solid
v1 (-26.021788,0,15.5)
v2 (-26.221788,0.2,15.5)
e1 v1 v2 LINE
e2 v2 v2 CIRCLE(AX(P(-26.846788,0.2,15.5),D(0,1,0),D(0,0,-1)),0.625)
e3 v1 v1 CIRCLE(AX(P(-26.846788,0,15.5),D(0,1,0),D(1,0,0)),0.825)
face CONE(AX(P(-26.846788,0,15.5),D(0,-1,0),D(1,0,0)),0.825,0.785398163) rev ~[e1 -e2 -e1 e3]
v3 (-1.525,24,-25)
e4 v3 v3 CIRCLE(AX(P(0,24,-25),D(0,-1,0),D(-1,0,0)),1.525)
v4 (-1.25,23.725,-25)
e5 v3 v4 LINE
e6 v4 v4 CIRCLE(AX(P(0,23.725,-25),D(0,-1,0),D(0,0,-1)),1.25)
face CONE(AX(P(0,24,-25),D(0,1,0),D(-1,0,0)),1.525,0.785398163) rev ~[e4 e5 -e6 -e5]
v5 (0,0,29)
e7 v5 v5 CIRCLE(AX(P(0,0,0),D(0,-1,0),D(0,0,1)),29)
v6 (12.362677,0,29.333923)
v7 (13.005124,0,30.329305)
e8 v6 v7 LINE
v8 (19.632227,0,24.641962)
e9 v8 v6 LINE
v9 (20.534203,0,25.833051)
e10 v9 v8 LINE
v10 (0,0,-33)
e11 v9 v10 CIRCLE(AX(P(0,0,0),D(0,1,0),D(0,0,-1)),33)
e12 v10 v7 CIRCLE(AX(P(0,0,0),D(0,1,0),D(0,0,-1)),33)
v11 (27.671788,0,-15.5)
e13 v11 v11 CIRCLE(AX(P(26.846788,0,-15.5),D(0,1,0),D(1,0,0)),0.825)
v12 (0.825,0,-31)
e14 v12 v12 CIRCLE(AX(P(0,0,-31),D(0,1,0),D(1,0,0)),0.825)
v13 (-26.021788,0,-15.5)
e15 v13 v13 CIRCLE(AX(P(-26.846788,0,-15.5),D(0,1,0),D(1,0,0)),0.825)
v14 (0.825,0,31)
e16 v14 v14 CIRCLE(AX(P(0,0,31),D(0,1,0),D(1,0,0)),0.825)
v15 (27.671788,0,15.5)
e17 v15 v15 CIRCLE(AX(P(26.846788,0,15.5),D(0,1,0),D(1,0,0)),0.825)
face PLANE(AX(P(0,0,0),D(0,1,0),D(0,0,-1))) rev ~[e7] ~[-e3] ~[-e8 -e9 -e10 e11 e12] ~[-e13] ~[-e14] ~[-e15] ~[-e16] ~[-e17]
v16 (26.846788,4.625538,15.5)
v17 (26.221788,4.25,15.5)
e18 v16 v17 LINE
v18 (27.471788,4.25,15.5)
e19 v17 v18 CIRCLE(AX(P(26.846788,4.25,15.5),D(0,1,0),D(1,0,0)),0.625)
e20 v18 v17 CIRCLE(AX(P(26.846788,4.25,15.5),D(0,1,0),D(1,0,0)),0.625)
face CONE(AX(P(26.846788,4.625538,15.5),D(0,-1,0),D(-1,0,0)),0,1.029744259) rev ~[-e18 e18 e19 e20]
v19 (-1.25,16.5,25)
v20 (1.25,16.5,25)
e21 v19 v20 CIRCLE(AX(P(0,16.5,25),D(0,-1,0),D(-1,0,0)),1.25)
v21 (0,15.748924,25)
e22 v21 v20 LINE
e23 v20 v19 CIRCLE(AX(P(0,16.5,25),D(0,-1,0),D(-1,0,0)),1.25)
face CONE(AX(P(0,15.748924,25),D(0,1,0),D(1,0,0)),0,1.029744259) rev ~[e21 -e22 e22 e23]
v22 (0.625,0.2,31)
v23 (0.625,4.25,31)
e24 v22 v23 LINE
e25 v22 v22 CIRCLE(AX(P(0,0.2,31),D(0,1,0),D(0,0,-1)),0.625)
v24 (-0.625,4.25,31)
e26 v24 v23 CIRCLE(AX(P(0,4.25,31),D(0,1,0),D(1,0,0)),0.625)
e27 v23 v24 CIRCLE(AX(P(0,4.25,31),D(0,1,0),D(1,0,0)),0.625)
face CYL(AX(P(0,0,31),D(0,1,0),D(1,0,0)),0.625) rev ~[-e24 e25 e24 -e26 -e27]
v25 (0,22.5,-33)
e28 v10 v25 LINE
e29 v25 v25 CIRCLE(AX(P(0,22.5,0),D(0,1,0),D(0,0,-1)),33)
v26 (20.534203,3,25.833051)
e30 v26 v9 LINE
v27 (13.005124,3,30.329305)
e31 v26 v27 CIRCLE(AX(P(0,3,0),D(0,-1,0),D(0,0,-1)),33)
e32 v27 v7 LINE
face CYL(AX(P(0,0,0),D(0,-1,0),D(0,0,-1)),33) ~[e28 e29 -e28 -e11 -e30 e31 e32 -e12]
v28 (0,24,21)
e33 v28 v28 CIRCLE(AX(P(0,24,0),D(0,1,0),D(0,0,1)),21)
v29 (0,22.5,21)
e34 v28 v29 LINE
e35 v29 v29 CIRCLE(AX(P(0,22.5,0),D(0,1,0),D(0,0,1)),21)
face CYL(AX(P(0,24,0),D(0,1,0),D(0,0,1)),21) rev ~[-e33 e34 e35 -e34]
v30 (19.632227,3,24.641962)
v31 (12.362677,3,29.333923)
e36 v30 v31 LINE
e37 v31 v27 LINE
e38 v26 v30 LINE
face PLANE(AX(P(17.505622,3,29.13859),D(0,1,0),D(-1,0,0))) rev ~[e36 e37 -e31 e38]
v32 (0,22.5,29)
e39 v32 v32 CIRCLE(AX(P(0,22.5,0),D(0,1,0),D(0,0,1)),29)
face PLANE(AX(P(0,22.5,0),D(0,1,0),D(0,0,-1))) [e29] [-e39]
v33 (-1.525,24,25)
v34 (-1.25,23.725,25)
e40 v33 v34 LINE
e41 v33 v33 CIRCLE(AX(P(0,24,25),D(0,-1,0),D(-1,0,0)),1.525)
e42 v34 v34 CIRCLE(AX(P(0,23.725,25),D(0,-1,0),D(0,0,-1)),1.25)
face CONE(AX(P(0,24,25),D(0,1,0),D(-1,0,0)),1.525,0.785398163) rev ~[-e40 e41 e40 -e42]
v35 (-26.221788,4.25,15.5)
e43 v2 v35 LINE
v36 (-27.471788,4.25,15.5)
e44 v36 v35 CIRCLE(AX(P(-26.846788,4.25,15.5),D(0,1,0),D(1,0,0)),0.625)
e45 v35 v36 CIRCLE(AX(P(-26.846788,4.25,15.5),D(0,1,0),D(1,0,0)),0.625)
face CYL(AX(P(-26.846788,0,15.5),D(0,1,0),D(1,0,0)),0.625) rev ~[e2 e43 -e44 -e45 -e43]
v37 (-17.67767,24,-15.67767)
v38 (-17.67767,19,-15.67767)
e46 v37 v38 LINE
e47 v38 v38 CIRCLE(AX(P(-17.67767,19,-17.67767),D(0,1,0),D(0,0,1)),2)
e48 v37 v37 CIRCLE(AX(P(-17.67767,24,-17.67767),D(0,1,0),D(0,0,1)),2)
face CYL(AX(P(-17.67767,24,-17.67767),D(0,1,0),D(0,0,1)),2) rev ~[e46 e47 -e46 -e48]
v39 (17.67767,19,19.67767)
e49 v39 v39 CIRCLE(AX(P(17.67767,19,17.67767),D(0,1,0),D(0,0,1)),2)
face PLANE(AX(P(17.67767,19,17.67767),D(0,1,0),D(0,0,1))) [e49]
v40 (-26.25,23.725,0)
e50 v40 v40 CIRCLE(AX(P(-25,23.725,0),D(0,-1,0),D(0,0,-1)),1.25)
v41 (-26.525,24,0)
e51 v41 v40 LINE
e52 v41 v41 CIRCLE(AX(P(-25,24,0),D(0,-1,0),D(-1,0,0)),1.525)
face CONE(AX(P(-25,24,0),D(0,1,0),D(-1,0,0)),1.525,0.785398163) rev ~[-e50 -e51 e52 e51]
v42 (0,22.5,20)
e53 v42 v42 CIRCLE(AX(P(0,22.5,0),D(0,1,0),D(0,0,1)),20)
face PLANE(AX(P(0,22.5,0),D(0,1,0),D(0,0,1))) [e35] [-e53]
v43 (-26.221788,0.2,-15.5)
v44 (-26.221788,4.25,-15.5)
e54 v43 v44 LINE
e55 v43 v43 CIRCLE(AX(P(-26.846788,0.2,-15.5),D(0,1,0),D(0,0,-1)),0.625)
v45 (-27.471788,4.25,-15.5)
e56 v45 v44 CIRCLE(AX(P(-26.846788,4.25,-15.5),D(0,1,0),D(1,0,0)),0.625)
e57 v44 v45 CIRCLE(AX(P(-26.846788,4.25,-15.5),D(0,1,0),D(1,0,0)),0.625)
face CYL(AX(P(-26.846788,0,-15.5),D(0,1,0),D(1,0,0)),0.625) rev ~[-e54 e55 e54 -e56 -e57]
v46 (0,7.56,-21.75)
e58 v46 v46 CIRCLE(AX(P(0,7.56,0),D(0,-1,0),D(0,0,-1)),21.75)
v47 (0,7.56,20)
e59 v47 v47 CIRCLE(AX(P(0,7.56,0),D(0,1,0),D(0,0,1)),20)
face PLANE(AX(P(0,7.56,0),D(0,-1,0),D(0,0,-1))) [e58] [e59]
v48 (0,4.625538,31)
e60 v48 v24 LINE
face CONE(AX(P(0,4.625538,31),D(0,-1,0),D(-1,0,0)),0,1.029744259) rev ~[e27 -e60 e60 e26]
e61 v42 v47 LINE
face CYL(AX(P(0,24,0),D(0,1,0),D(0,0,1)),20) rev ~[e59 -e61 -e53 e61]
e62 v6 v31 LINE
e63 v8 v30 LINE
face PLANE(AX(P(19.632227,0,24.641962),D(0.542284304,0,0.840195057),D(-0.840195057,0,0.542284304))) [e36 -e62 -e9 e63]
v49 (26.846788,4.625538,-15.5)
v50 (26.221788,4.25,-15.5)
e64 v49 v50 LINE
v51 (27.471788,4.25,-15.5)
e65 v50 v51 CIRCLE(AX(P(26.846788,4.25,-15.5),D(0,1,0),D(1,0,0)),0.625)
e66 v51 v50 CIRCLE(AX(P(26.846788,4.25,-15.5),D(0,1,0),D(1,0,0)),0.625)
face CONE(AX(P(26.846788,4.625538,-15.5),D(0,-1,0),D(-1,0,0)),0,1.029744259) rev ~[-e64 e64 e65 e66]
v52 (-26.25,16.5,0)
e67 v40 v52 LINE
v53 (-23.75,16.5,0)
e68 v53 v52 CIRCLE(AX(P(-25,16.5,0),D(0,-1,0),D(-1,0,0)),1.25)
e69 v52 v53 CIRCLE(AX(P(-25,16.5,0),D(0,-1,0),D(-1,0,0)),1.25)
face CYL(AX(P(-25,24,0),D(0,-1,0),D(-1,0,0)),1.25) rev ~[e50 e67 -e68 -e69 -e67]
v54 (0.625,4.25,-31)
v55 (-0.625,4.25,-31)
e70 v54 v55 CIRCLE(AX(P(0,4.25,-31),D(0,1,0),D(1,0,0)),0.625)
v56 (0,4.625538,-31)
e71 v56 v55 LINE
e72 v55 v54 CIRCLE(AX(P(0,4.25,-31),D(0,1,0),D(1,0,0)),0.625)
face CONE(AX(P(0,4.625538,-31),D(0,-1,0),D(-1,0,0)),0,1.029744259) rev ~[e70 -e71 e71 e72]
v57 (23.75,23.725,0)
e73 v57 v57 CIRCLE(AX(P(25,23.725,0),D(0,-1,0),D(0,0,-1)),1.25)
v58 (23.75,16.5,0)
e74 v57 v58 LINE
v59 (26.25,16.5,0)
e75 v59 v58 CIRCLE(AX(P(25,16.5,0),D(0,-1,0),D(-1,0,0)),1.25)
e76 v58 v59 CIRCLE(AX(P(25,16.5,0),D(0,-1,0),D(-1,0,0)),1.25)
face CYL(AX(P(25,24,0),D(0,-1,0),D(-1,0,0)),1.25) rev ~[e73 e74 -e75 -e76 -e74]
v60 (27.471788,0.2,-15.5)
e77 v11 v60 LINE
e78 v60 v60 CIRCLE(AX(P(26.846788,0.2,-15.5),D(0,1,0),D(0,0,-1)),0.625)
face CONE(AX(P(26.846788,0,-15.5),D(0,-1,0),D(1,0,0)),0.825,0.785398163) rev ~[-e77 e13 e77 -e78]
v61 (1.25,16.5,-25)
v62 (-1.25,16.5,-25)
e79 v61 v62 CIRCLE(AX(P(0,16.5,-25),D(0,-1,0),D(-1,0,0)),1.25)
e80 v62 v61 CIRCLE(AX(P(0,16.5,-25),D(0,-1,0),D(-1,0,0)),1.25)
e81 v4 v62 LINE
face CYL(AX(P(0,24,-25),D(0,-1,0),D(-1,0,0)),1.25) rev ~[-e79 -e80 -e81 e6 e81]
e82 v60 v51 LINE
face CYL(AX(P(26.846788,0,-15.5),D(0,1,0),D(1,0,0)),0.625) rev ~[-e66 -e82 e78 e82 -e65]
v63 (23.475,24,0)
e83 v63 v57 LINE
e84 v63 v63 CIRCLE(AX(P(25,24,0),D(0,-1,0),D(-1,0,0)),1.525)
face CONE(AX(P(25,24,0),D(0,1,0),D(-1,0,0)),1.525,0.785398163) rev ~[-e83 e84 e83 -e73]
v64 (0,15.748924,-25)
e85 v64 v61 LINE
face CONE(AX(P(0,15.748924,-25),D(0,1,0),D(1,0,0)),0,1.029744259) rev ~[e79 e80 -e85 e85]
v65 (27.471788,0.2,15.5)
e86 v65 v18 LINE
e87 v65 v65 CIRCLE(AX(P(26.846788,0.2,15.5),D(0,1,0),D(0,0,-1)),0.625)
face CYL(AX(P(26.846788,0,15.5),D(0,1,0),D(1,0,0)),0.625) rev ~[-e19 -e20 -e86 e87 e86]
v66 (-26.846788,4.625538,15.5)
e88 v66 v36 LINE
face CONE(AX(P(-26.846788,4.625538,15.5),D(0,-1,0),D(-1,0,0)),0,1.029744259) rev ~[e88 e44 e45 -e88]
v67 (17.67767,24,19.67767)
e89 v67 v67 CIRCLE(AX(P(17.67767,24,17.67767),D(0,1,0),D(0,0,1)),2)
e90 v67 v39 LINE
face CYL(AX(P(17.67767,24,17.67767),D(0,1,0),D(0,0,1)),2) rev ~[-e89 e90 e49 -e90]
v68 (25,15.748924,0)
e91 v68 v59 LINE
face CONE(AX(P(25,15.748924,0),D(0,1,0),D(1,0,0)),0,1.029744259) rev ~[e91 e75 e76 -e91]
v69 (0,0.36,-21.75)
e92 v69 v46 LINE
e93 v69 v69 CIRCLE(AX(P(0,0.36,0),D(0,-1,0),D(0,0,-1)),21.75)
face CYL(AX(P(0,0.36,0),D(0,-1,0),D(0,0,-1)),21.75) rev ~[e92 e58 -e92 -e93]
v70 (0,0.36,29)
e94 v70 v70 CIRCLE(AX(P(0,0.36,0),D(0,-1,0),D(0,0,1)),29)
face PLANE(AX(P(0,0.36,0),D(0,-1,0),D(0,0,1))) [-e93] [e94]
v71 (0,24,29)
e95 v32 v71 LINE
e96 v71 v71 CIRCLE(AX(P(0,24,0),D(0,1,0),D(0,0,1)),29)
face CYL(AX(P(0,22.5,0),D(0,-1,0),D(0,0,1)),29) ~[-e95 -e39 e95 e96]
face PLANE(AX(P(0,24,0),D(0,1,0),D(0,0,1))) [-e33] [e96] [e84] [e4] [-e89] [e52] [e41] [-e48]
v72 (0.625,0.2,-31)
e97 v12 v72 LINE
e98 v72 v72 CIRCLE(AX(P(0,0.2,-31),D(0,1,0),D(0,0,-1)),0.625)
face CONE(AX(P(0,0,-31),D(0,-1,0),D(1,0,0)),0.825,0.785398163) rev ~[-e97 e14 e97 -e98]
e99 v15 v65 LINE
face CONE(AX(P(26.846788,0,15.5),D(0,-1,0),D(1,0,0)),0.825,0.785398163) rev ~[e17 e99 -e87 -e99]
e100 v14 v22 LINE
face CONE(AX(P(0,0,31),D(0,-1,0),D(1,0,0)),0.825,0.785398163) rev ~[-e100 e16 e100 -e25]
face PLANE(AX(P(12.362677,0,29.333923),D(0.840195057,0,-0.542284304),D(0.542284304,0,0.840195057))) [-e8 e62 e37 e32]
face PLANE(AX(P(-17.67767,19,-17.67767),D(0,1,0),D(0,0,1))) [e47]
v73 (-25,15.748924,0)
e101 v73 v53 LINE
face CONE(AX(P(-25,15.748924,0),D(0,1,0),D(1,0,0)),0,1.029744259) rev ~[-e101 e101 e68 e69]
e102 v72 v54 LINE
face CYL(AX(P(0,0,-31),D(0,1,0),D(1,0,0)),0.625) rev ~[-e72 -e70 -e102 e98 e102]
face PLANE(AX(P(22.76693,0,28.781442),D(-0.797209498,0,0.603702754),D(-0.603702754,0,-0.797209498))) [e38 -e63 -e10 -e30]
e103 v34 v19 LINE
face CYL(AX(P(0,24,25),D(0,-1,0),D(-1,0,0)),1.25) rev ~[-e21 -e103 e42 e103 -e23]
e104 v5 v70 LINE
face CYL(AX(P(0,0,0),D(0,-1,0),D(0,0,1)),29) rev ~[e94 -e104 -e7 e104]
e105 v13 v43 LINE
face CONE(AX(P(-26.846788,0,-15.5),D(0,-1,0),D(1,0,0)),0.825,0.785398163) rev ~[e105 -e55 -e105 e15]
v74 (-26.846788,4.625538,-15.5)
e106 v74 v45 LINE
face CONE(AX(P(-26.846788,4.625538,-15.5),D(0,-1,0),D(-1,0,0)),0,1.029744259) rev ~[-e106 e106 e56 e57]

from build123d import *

# Parameters (mm, degrees)
SKETCH1_R                     = 33
BOSS_EXTRUDE1_DEPTH           = 22.5
SKETCH2_R                     = 29
BOSS_EXTRUDE2_DEPTH           = 1.5
SKETCH3_R                     = 20
CUT_EXTRUDE1_DEPTH            = 58.5
M3_TAPPED_HOLE1_D             = 2.5
M3_TAPPED_HOLE1_DEPTH         = 7.5
M3_TAPPED_HOLE1_CSINK_D       = 3.05
M3_TAPPED_HOLE1_CSINK_ANGLE   = 90
M3_TAPPED_HOLE1_TIP           = 0.751075774
SKETCH7_R                     = 2
CUT_EXTRUDE2_DEPTH            = 5
SKETCH8_R                     = 21
CUT_EXTRUDE3_DEPTH            = 1.5
SKETCH9_R                     = 29
CUT_EXTRUDE4_DEPTH            = 0.36
SKETCH10_R                    = 21.75
CUT_EXTRUDE5_DEPTH            = 7.2
M1_6_TAPPED_HOLE1_D           = 1.25
M1_6_TAPPED_HOLE1_DEPTH       = 4.25
M1_6_TAPPED_HOLE1_CSINK_D     = 1.65
M1_6_TAPPED_HOLE1_CSINK_ANGLE = 90
M1_6_TAPPED_HOLE1_TIP         = 0.375537887
CUT_EXTRUDE6_DEPTH            = 3


with BuildPart() as part:
    # Sketch1 → Boss-Extrude1 (new body)
    with BuildSketch(Plane(origin=(0, 0, 0), x_dir=(1, 0, 0), z_dir=(0, 1, 0))):
        with Locations(Location((0, 0, 0), (0, 0, 90))):
            Circle(SKETCH1_R)
    extrude(amount=BOSS_EXTRUDE1_DEPTH)

    # Sketch2 → Boss-Extrude2 (add)
    with BuildSketch(Plane(origin=(0, 22.5, 0), x_dir=(1, 0, 0), z_dir=(0, 1, 0))):
        with Locations(Location((0, 0, 0), (0, 0, 270))):
            Circle(SKETCH2_R)
    extrude(amount=BOSS_EXTRUDE2_DEPTH)

    # Sketch3 → Cut-Extrude1 (cut)
    with BuildSketch(Plane(origin=(0, 24, 0), x_dir=(1, 0, 0), z_dir=(0, 1, 0))):
        with Locations(Location((0, 0, 0), (0, 0, 270))):
            Circle(SKETCH3_R)
    extrude(amount=-CUT_EXTRUDE1_DEPTH, mode=Mode.SUBTRACT)

    # M3 Tapped Hole1
    with Locations(Plane(origin=(0, 24, 0), x_dir=(1, 0, 0), z_dir=(0, 1, 0))):
        with Locations((25, 0), (0, 25), (-25, 0), (0, -25)):
            CounterSinkHole(M3_TAPPED_HOLE1_D / 2, M3_TAPPED_HOLE1_CSINK_D / 2, depth=M3_TAPPED_HOLE1_DEPTH, counter_sink_angle=M3_TAPPED_HOLE1_CSINK_ANGLE)
            with Locations((0, 0, -(M3_TAPPED_HOLE1_DEPTH + M3_TAPPED_HOLE1_TIP / 2))):  # 118° drill point
                Cone(0, M3_TAPPED_HOLE1_D / 2, M3_TAPPED_HOLE1_TIP, mode=Mode.SUBTRACT)

    # Sketch7 → Cut-Extrude2 (cut)
    with BuildSketch(Plane(origin=(0, 24, 0), x_dir=(1, 0, 0), z_dir=(0, 1, 0))):
        with Locations(Location((-17.67766953, 17.67766953, 0), (0, 0, 270))):
            Circle(SKETCH7_R)
        with Locations(Location((17.67766953, -17.67766953, 0), (0, 0, 270))):
            Circle(SKETCH7_R)
    extrude(amount=-CUT_EXTRUDE2_DEPTH, mode=Mode.SUBTRACT)

    # Sketch8 → Cut-Extrude3 (cut)
    with BuildSketch(Plane(origin=(0, 24, 0), x_dir=(1, 0, 0), z_dir=(0, 1, 0))):
        with Locations(Location((0, 0, 0), (0, 0, 270))):
            Circle(SKETCH8_R)
    extrude(amount=-CUT_EXTRUDE3_DEPTH, mode=Mode.SUBTRACT)

    # Sketch9 → Cut-Extrude4 (cut)
    with BuildSketch(Plane.XZ):
        with Locations(Location((0, 0, 0), (0, 0, 90))):
            Circle(SKETCH9_R)
    extrude(amount=-CUT_EXTRUDE4_DEPTH, mode=Mode.SUBTRACT)

    # Sketch10 → Cut-Extrude5 (cut)
    with BuildSketch(Plane.XZ.offset(-0.36)):
        with Locations(Location((0, 0, 0), (0, 0, 270))):
            Circle(SKETCH10_R)
    extrude(amount=-CUT_EXTRUDE5_DEPTH, mode=Mode.SUBTRACT)

    # M1.6 Tapped Hole1
    with Locations(Plane(origin=(0, 0, 0), x_dir=(-1, 0, 0), z_dir=(0, -1, 0))):
        with Locations((0, 0), (0, 31), (26.846787517, 15.5), (26.846787517, -15.5), (0, -31), (-26.846787517, -15.5), (-26.846787517, 15.5)):
            CounterSinkHole(M1_6_TAPPED_HOLE1_D / 2, M1_6_TAPPED_HOLE1_CSINK_D / 2, depth=M1_6_TAPPED_HOLE1_DEPTH, counter_sink_angle=M1_6_TAPPED_HOLE1_CSINK_ANGLE)
            with Locations((0, 0, -(M1_6_TAPPED_HOLE1_DEPTH + M1_6_TAPPED_HOLE1_TIP / 2))):  # 118° drill point
                Cone(0, M1_6_TAPPED_HOLE1_D / 2, M1_6_TAPPED_HOLE1_TIP, mode=Mode.SUBTRACT)

    # Sketch15 → Cut-Extrude6 (cut)
    with BuildSketch(Plane.XZ):
        Polygon((19.632226772, 24.641961986), (12.362677286, 29.333923153), (15.170555531, 33.68434489), (22.766930333, 28.781441946), align=None)
    extrude(amount=-CUT_EXTRUDE6_DEPTH, mode=Mode.SUBTRACT)


solid = part.part
